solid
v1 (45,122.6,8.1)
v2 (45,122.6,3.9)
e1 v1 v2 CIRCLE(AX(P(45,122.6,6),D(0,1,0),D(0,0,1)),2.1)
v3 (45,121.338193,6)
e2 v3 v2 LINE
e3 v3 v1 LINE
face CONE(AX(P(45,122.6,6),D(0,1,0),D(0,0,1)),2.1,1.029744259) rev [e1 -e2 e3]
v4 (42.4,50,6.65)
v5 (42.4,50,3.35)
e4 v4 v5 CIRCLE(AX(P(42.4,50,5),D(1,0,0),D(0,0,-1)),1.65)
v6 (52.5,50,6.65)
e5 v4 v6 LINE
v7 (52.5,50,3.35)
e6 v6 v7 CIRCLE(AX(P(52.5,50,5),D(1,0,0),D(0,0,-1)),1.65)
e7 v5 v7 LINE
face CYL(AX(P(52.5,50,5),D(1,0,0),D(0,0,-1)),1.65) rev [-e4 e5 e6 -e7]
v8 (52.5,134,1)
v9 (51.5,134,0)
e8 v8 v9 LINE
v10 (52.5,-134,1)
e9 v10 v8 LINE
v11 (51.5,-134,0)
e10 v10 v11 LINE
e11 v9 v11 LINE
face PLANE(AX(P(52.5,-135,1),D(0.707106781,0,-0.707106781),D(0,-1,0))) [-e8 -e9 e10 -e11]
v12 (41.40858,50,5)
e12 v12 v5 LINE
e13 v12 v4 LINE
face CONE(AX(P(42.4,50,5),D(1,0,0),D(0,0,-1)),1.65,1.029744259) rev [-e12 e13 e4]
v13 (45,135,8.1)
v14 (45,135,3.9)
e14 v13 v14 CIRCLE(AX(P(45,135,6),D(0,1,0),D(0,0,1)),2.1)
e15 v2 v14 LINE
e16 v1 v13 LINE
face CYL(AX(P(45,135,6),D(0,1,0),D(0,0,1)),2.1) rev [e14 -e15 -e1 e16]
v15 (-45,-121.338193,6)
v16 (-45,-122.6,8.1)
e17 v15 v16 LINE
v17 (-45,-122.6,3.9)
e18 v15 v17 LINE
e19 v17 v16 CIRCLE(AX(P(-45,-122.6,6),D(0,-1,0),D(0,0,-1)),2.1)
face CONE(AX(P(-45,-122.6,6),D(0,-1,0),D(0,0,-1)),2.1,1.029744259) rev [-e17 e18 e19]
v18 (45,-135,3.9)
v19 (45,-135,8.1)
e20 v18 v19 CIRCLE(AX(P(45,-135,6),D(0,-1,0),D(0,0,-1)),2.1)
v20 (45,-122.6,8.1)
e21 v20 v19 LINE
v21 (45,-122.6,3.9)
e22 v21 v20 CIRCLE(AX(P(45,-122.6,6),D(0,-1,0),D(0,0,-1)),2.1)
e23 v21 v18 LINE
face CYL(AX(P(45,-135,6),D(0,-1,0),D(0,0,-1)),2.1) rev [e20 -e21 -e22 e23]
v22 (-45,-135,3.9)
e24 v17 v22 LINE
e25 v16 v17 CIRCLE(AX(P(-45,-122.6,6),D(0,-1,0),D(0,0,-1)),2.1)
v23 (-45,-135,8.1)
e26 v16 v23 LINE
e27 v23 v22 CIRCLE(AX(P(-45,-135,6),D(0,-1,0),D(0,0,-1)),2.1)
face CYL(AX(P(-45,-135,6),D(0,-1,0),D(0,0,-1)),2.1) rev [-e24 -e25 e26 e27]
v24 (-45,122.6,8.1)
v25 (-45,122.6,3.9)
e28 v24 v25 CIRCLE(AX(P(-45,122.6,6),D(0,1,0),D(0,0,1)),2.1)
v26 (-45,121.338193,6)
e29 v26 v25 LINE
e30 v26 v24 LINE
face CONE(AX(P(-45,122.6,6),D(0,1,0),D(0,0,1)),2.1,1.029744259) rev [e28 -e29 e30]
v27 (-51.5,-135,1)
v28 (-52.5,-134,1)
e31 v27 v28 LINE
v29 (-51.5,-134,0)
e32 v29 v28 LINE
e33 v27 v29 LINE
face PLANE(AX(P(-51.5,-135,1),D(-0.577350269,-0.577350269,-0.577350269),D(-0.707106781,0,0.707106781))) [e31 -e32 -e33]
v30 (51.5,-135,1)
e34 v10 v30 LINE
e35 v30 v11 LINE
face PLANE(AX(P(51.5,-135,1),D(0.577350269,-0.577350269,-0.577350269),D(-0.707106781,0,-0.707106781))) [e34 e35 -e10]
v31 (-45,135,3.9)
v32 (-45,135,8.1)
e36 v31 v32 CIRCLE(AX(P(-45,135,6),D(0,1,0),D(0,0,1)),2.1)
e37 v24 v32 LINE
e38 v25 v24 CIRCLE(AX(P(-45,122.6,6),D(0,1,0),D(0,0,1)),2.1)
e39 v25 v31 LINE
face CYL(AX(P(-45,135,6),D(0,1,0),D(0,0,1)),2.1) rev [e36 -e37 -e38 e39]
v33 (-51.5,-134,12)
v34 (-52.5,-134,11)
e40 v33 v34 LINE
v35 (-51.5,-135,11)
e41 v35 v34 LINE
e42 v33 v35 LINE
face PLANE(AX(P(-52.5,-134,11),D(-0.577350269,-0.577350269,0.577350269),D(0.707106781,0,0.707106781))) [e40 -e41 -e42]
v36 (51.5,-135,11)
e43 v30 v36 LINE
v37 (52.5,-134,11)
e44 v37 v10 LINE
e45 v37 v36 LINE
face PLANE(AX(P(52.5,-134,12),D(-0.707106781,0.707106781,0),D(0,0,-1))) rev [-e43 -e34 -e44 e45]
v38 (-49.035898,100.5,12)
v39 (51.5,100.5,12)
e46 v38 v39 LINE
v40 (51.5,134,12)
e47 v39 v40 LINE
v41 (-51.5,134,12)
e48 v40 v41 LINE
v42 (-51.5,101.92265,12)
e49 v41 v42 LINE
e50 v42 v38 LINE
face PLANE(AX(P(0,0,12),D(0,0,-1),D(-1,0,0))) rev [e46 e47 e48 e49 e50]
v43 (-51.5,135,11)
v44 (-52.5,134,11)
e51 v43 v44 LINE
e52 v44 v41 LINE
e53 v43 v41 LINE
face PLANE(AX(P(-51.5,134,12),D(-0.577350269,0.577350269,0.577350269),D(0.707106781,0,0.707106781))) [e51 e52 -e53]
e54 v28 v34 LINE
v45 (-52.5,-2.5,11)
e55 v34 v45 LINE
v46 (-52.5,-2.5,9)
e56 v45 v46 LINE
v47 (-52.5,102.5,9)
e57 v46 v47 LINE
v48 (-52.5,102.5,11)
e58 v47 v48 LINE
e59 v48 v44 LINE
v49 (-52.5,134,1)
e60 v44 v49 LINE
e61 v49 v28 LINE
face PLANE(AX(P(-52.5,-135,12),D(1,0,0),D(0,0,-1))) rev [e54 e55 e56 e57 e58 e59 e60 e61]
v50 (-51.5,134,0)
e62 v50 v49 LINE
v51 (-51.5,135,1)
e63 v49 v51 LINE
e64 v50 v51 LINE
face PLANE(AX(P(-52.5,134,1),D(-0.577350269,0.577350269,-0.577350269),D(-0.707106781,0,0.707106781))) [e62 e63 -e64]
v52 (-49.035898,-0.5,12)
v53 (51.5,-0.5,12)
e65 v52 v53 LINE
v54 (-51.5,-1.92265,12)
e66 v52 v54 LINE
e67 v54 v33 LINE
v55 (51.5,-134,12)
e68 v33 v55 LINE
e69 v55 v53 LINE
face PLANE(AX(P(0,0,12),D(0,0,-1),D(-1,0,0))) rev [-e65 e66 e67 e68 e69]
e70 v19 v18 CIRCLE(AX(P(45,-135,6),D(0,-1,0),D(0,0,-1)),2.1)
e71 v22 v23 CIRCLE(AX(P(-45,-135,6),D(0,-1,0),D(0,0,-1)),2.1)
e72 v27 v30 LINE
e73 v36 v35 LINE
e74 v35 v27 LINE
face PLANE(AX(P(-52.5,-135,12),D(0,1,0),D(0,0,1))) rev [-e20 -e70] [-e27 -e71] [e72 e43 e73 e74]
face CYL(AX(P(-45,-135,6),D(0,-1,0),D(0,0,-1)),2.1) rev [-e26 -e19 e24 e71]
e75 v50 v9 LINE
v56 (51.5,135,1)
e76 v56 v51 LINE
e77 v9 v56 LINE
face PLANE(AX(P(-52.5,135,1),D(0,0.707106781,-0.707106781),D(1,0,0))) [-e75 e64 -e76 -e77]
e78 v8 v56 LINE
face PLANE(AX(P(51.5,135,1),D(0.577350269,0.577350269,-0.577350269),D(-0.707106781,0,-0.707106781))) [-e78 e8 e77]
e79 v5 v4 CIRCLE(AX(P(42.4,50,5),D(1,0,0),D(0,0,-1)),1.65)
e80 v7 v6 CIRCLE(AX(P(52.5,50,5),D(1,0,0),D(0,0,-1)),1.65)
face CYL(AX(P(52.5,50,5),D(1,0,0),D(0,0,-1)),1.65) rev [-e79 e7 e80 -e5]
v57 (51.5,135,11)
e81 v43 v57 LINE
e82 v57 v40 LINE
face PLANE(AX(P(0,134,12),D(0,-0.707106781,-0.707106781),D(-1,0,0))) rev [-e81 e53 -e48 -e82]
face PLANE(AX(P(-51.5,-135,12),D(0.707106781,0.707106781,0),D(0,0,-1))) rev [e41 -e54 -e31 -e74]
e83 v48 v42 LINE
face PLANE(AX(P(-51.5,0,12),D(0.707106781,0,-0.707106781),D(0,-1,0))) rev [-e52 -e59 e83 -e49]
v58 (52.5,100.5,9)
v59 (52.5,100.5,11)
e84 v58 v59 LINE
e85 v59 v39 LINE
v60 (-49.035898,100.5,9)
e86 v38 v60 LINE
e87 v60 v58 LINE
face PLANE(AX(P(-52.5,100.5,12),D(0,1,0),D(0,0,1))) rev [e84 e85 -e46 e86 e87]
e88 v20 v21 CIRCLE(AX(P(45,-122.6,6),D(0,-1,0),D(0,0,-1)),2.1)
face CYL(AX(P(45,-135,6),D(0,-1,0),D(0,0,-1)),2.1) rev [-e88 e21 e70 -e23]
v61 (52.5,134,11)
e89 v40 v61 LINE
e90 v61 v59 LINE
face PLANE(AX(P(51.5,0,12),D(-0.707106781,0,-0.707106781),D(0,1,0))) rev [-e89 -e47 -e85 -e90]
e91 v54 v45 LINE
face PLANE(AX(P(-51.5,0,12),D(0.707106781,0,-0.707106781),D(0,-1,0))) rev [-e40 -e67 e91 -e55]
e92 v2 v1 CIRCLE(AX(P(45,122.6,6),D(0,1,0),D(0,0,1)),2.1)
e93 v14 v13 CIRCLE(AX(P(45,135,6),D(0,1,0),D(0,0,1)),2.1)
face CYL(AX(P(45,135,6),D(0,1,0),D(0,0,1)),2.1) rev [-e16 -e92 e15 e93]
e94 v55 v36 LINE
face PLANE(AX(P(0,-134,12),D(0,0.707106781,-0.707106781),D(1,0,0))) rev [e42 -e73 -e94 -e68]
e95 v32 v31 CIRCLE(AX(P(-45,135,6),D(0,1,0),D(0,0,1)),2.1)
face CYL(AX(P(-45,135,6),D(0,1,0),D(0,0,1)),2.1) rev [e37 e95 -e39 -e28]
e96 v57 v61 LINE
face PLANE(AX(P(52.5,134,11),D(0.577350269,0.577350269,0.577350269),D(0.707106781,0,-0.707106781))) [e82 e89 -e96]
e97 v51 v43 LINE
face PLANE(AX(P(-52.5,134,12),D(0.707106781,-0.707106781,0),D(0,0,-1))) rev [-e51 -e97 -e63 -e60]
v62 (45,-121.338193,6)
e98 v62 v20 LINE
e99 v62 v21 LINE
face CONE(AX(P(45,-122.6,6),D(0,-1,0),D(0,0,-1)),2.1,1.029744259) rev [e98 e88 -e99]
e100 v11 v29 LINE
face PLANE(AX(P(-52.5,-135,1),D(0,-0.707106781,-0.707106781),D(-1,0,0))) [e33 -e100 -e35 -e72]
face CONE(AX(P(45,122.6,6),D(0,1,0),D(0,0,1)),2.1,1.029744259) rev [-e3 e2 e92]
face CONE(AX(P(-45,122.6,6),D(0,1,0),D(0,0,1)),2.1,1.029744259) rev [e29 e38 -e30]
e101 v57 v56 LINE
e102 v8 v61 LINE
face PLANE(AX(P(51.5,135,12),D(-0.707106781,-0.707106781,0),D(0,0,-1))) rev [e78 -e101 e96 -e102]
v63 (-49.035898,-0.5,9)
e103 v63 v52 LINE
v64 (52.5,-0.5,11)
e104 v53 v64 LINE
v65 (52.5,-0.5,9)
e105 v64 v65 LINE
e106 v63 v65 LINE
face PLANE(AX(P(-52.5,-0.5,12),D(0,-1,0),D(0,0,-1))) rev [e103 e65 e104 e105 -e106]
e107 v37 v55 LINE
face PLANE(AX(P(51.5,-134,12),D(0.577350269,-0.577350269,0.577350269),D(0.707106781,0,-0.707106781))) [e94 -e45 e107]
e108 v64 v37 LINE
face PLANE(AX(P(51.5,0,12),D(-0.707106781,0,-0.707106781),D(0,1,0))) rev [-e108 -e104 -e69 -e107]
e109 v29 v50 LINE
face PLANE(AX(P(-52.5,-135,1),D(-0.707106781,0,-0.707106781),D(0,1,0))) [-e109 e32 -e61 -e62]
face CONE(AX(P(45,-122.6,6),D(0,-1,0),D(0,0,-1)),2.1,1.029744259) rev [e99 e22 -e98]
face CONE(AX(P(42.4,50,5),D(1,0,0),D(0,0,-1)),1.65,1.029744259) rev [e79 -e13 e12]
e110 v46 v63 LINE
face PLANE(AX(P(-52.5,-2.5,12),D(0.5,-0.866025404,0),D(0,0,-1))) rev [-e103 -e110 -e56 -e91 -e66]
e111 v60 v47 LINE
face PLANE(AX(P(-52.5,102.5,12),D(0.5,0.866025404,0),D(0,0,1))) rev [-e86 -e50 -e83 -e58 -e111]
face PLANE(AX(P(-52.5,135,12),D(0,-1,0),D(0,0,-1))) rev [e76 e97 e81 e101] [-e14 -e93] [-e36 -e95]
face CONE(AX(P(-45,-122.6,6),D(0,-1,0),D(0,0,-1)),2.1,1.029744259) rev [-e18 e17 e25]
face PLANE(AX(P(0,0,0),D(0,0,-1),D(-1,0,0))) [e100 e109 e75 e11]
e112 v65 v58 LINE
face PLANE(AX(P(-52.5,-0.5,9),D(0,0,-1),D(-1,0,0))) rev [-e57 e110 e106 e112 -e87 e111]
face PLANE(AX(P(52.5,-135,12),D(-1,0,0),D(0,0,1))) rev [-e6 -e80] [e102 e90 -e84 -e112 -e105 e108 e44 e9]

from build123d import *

# Parameters (mm, degrees)
SKETCH_1_W                  = 105
SKETCH_1_H                  = 270
EXTRUDE_1_DEPTH             = 12
SKETCH_2_W                  = 3
SKETCH_2_H                  = 101
CUT_EXTRUDE_1_DEPTH         = 172.446784747
HOLE_WIZARD_M5_1_AT_2_COUNT = 2
HOLE_WIZARD_M5_1_AT_2_PITCH = 90
CHAMFER_1_SIZE              = 1
CHAMFER_2_SIZE              = 2
CHAMFER_2_SIZE2             = 3.464101615
HOLE_WIZARD_M4_1_D          = 3.3
HOLE_WIZARD_M4_1_DEPTH      = 10.1
HOLE_WIZARD_M4_1_TIP        = 0.991420021


with BuildPart() as part:
    # 草图1 → 凸台-拉伸1 (new body)
    with BuildSketch(Plane.XY):
        Rectangle(SKETCH_1_W, SKETCH_1_H)
    extrude(amount=EXTRUDE_1_DEPTH)

    # 草图2 → 切除-拉伸1 (cut, through all)
    with BuildSketch(Plane(origin=(52.5, 0, 0), x_dir=(0, 0, -1), z_dir=(1, 0, 0))):
        with Locations((-10.5, 50)):
            Rectangle(SKETCH_2_W, SKETCH_2_H)
    extrude(amount=-CUT_EXTRUDE_1_DEPTH, mode=Mode.SUBTRACT)

    # 草图4 → M5 螺纹孔1 (revolve, cut)
    with BuildSketch(Plane(origin=(-45, -135, 6), x_dir=(0, 0, -1), z_dir=(1, 0, 0))):
        Polygon((0, 0), (0, 13.6618073), (2.1, 12.4), (2.1, 0), align=None)
    hole_wizard_m5_1 = revolve(axis=Axis((-45, -141.35, 6), (0, 1, 0)), mode=Mode.SUBTRACT)

    # M5 螺纹孔1 at 2: M5 螺纹孔1 ×2
    with Locations(*[(i * HOLE_WIZARD_M5_1_AT_2_PITCH, 0, 0) for i in range(1, HOLE_WIZARD_M5_1_AT_2_COUNT)]):
        add(hole_wizard_m5_1, mode=Mode.SUBTRACT)

    # 镜向1: M5 螺纹孔1 across plane
    add(hole_wizard_m5_1.mirror(Plane.ZX), mode=Mode.SUBTRACT)

    # 镜向1 copy 1 sketch → 镜向1 copy 1 (revolve, cut)
    with BuildSketch(Plane(origin=(45, 135, 6), x_dir=(0, 0, -1), z_dir=(1, 0, 0))):
        Polygon((0, 0), (0, -13.6618073), (2.1, -12.4), (2.1, 0), align=None)
    revolve(axis=Axis((45, 141.35, 6), (0, 1, 0)), mode=Mode.SUBTRACT)

    # 倒角1
    chamfer_1_edges = [part.edges().sort_by_distance(p)[0] for p in [
        (-52.5, 117.75, 12),
        (0, -135, 12),
        (52.5, 117.75, 12),
        (-52.5, -67.75, 12),
        (52.5, -67.75, 12),
        (0, -135, 0),
        (-52.5, 0, 0),
        (0, 135, 0),
        (52.5, 0, 0),
        (0, 135, 12),
        (52.5, -135, 6),
        (-52.5, -135, 6),
        (-52.5, 135, 6),
        (52.5, 135, 6),
    ]]
    chamfer(chamfer_1_edges, length=CHAMFER_1_SIZE)

    # 倒角2
    chamfer_2_edges = [part.edges().sort_by_distance(p)[0] for p in [
        (-52.5, -0.5, 10),
        (-52.5, 100.5, 10),
    ]]
    chamfer_2_side = [part.faces().sort_by_distance(p)[0] for p in [
        (-52.5, -4.075867635, 5.673930589),
    ]]
    chamfer(chamfer_2_edges, length=CHAMFER_2_SIZE, length2=CHAMFER_2_SIZE2, reference=chamfer_2_side[0])

    # M4 螺纹孔1
    with Locations(Plane(origin=(52.5, 0, 0), x_dir=(0, 0, -1), z_dir=(1, 0, 0))):
        with Locations((-5, 50)):
            Hole(HOLE_WIZARD_M4_1_D / 2, depth=HOLE_WIZARD_M4_1_DEPTH)
            with Locations((0, 0, -(HOLE_WIZARD_M4_1_DEPTH + HOLE_WIZARD_M4_1_TIP / 2))):  # 118° drill point
                Cone(0, HOLE_WIZARD_M4_1_D / 2, HOLE_WIZARD_M4_1_TIP, mode=Mode.SUBTRACT)


solid = part.part
